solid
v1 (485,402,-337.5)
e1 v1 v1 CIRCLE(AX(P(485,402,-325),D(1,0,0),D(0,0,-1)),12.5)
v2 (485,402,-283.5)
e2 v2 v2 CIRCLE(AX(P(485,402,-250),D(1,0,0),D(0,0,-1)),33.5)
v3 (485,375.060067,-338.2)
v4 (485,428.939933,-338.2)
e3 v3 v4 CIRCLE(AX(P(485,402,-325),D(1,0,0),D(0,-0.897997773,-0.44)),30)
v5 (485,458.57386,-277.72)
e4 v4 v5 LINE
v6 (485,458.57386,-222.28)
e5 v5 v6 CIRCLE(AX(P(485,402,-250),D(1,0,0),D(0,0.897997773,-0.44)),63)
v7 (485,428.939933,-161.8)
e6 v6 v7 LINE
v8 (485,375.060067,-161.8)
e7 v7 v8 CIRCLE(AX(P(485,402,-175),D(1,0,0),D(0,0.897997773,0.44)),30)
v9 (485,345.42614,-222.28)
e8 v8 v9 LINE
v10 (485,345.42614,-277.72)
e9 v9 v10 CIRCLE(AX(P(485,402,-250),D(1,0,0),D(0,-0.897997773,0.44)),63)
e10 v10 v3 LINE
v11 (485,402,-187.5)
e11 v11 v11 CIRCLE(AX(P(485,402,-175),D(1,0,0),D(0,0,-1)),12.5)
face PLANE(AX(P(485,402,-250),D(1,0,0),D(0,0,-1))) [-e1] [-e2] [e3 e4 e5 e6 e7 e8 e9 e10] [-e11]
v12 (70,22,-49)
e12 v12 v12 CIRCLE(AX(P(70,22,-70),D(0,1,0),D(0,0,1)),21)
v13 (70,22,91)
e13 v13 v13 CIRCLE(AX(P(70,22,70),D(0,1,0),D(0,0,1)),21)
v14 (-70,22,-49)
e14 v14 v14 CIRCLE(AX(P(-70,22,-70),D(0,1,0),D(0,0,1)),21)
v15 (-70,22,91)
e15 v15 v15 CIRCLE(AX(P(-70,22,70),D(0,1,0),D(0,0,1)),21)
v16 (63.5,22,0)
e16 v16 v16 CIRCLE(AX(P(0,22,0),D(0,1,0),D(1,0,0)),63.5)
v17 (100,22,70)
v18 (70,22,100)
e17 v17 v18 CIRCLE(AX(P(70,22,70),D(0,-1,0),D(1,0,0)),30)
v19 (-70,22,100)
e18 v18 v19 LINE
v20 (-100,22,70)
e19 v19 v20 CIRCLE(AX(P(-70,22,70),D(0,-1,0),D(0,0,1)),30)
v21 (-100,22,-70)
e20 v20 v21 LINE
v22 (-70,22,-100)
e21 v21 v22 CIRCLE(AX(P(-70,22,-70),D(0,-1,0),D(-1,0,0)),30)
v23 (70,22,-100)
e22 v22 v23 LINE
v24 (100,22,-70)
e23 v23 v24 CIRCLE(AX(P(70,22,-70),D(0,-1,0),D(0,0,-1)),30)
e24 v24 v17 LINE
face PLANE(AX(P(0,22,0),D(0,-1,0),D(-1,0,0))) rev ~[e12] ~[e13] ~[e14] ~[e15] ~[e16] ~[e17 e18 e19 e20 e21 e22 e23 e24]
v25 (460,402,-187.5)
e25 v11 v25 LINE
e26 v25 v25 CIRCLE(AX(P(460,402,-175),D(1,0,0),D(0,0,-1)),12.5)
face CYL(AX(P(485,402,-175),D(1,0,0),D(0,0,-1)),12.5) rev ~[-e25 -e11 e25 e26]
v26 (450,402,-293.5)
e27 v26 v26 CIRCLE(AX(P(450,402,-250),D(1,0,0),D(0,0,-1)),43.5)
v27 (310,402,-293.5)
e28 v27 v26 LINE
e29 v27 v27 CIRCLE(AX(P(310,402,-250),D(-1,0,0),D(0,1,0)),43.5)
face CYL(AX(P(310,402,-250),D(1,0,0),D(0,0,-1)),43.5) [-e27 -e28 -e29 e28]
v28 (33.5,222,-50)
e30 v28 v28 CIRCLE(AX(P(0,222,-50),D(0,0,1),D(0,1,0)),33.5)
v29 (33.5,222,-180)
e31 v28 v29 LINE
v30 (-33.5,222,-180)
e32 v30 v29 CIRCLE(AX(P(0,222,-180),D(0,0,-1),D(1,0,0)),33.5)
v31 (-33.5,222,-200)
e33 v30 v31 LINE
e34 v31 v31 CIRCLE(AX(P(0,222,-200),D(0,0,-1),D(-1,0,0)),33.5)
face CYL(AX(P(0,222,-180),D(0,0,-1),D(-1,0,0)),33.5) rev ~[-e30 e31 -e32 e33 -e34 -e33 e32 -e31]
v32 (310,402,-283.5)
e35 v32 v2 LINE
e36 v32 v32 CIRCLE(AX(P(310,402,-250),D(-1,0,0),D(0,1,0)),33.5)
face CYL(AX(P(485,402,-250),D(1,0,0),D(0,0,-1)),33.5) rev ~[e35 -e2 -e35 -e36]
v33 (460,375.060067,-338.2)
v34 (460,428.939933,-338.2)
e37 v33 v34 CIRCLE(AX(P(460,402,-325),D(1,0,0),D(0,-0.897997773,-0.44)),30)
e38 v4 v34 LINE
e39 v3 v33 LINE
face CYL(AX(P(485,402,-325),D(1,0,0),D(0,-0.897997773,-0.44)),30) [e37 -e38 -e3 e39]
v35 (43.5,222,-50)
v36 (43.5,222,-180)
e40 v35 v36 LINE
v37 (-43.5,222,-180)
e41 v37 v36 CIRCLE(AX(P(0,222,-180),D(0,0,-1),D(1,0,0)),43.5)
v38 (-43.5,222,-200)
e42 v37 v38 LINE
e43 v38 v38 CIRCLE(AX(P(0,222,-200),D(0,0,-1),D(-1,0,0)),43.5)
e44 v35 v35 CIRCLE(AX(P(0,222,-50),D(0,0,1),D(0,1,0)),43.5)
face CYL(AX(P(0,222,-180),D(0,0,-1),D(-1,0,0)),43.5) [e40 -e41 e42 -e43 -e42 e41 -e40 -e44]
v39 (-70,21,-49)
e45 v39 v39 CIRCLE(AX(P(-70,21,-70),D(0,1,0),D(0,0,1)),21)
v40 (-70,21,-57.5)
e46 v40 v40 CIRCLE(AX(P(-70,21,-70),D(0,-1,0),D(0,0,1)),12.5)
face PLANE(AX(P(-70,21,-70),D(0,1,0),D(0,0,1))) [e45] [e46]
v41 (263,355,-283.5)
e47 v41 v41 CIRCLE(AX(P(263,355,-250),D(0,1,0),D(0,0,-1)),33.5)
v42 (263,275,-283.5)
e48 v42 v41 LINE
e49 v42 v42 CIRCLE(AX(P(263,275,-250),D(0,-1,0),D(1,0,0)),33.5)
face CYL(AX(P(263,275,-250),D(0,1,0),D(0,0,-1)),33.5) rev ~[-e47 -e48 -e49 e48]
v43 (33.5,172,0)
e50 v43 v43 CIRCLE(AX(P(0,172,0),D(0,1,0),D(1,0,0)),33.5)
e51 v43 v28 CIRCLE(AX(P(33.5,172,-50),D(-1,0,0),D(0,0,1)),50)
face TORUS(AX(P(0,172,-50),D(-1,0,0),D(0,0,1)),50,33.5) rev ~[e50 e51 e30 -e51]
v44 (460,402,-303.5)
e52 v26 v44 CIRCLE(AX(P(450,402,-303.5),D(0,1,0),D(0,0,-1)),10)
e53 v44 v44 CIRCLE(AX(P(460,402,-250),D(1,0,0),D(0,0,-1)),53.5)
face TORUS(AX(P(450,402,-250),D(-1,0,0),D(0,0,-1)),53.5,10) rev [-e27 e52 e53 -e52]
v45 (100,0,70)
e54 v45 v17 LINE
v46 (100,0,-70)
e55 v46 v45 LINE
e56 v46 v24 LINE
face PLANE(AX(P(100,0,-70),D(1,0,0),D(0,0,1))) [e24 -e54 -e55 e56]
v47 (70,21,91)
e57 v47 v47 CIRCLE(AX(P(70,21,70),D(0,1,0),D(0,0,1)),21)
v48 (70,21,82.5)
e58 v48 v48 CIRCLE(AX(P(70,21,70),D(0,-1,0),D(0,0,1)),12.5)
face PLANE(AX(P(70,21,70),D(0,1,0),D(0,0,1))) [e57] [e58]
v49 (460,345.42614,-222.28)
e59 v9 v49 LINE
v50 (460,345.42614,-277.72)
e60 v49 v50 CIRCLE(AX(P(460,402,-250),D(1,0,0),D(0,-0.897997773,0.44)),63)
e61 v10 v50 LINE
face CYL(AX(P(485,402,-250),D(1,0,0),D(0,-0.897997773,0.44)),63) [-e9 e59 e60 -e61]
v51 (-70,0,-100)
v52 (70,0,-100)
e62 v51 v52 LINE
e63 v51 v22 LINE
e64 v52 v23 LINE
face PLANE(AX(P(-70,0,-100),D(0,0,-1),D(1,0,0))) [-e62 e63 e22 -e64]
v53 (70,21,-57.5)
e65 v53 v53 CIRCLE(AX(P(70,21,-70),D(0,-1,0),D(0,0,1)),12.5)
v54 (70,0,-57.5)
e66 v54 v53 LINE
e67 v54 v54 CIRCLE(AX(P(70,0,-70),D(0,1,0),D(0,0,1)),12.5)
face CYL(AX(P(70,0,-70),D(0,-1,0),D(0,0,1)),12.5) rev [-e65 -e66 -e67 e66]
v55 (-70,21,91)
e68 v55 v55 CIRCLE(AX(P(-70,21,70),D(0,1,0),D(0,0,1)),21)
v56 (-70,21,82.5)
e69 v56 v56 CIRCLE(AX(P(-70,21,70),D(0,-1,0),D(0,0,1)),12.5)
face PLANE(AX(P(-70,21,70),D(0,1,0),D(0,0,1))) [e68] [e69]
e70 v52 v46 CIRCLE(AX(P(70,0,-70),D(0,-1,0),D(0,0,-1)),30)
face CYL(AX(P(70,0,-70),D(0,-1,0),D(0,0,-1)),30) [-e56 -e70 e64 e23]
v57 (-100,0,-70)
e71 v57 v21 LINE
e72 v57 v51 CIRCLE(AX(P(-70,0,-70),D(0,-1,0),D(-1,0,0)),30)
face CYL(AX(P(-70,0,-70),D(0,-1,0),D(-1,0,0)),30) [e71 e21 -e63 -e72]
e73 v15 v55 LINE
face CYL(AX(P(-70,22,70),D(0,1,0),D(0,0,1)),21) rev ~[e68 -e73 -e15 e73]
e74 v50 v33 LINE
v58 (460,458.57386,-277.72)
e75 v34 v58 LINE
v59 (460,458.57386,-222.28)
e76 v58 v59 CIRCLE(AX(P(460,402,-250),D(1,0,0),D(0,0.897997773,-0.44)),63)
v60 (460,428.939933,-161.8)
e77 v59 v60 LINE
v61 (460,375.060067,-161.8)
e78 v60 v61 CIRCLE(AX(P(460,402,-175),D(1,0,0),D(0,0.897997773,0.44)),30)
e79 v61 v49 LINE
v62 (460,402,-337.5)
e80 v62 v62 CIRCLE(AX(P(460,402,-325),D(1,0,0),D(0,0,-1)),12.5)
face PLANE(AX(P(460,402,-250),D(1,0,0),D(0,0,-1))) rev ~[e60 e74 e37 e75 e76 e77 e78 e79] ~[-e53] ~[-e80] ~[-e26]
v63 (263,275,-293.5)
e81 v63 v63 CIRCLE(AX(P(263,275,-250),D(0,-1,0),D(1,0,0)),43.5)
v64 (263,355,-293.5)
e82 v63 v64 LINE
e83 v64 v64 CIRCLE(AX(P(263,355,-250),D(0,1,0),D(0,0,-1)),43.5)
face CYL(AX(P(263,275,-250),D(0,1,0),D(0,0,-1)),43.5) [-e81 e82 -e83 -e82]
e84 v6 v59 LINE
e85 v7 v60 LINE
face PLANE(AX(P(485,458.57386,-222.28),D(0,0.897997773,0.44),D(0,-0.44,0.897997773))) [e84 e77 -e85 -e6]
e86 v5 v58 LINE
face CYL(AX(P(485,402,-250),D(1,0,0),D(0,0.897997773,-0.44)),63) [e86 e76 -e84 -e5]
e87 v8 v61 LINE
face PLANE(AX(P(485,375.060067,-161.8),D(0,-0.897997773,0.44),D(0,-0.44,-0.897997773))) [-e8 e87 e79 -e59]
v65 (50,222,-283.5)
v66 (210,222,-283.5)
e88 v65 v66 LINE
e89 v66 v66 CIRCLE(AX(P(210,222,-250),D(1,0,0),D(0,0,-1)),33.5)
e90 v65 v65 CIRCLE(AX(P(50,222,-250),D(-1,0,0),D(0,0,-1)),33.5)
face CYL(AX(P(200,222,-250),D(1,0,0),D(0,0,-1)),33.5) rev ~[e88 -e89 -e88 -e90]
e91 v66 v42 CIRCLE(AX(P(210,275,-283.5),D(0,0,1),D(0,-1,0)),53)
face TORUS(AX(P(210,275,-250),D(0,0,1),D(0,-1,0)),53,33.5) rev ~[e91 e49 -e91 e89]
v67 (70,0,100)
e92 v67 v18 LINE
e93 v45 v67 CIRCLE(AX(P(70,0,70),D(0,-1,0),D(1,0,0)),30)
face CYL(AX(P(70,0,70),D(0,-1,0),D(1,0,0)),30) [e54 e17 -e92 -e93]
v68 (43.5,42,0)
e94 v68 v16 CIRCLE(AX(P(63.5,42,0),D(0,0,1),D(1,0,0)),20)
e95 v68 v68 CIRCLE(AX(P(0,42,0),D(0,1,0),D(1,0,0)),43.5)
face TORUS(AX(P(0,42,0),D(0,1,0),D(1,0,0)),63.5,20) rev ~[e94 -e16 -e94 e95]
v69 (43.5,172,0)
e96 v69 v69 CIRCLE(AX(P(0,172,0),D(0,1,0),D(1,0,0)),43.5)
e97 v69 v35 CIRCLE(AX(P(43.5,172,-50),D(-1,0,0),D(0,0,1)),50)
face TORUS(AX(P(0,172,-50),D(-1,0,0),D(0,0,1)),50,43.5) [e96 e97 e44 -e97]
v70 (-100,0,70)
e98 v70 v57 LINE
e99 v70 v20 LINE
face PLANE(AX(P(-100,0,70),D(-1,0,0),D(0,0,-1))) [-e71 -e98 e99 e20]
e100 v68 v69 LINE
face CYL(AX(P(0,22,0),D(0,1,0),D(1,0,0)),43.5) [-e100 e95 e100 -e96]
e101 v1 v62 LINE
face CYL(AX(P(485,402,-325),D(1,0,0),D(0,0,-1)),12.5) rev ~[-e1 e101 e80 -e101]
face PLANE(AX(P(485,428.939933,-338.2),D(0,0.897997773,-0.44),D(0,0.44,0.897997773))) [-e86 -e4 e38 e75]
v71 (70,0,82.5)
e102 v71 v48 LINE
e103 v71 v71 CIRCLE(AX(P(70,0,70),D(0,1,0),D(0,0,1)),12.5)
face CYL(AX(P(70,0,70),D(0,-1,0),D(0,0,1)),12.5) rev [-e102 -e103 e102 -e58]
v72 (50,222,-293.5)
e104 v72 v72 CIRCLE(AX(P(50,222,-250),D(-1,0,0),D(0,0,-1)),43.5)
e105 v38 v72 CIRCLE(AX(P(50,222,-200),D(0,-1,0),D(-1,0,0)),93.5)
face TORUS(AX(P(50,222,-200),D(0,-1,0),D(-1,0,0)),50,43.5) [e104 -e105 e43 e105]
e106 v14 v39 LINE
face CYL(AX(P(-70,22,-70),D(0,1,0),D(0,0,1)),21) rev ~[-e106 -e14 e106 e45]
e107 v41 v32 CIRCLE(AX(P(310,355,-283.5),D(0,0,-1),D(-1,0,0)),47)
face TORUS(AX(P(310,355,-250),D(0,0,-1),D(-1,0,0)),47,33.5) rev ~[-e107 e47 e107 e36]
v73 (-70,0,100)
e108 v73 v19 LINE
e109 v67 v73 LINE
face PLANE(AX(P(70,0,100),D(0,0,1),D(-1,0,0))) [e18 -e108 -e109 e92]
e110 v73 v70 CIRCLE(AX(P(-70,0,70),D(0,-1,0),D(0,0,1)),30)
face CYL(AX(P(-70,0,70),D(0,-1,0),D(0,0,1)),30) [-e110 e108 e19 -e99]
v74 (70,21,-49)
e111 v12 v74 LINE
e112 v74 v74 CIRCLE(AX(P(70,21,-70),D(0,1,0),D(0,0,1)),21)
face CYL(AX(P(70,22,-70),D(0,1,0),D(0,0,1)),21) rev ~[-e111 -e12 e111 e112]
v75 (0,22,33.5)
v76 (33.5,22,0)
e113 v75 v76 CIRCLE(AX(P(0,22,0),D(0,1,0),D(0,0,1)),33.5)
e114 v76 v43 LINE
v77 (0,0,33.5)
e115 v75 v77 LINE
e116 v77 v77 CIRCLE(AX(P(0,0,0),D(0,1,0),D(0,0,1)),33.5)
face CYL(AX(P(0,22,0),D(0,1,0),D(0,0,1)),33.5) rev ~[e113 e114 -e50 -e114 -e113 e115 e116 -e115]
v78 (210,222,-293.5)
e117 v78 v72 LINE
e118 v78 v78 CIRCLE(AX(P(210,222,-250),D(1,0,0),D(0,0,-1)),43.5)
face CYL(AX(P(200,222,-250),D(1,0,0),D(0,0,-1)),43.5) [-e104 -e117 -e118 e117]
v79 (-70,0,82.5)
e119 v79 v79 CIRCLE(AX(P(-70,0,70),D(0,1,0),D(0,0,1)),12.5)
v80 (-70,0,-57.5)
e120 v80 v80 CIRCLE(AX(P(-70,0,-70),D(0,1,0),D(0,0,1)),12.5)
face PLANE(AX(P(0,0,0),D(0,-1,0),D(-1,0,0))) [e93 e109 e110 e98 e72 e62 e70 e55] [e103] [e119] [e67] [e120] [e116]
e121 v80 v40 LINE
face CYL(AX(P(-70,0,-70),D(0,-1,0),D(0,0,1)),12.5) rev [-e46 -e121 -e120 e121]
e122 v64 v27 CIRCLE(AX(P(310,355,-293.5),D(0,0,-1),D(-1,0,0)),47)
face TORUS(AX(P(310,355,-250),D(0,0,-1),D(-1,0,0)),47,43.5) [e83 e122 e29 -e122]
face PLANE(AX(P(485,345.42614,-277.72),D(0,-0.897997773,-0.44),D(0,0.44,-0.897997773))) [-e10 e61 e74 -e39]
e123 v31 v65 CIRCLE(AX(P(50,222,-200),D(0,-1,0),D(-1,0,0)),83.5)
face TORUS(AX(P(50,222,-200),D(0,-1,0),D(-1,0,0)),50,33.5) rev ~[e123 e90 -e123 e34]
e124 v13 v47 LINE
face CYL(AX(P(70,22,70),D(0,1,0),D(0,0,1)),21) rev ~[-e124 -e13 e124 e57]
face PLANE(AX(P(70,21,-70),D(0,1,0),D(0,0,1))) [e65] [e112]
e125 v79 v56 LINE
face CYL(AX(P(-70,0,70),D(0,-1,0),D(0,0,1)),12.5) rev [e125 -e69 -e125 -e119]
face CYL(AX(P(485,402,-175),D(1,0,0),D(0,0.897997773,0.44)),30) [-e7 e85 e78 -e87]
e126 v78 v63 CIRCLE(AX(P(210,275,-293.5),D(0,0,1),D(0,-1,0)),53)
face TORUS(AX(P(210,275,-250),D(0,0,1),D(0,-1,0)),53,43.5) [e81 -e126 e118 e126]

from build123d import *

# Parameters (mm, degrees)
INLET_FLANGE_SKETCH_R         = 12.5
INLET_FLANGE_200X200X22_DEPTH = 22
BOLT_SPOTFACE_SKETCH_R        = 21
BOLT_SPOTFACES_4X_42_DEPTH    = 1
INLET_BORE_SKETCH_R           = 33.5
INLET_BORE_67_DEPTH           = 25
PIPE_SECTION_1_PROFILE_R      = 43.5
PIPE_SECTION_1_PROFILE_R_2    = 33.5
PIPE_SECTION_2_PROFILE_R      = 43.5
PIPE_SECTION_2_PROFILE_R_2    = 33.5
S_BEND_PROFILE_R              = 43.5
S_BEND_PROFILE_R_2            = 33.5
OUTLET_START                  = 25
OUTLET_FLANGE_SKETCH_R        = 33.5
OUTLET_FLANGE_SKETCH_R_2      = 12.5
OUTLET_FLANGE_DEPTH           = 25
INLET_FLANGE_FILLET_R20_R     = 20
OUTLET_FILLET_R10_R           = 10


with BuildPart() as part:
    # Inlet Flange Sketch → Inlet Flange 200x200x22 (new body)
    with BuildSketch(Plane(origin=(0, 0, 0), x_dir=(1, 0, 0), z_dir=(0, 1, 0))):
        with BuildLine():
            Line((-70, 100), (70, 100))
            ThreePointArc((70, 100), (91.213203436, 91.213203436), (100, 70))
            Line((100, 70), (100, -70))
            ThreePointArc((100, -70), (91.213203436, -91.213203436), (70, -100))
            Line((70, -100), (-70, -100))
            ThreePointArc((-70, -100), (-91.213203436, -91.213203436), (-100, -70))
            Line((-100, -70), (-100, 70))
            ThreePointArc((-100, 70), (-91.213203436, 91.213203436), (-70, 100))
        make_face()
        with Locations(Location((-70, 70, 0), (0, 0, 270))):
            Circle(INLET_FLANGE_SKETCH_R, mode=Mode.SUBTRACT)
        with Locations(Location((70, 70, 0), (0, 0, 270))):
            Circle(INLET_FLANGE_SKETCH_R, mode=Mode.SUBTRACT)
        with Locations(Location((70, -70, 0), (0, 0, 270))):
            Circle(INLET_FLANGE_SKETCH_R, mode=Mode.SUBTRACT)
        with Locations(Location((-70, -70, 0), (0, 0, 270))):
            Circle(INLET_FLANGE_SKETCH_R, mode=Mode.SUBTRACT)
    extrude(amount=INLET_FLANGE_200X200X22_DEPTH)

    # Bolt Spotface Sketch → Bolt Spotfaces 4xØ42 (cut)
    with BuildSketch(Plane(origin=(0, 22, 0), x_dir=(1, 0, 0), z_dir=(0, 1, 0))):
        with Locations(Location((-70, 70, 0), (0, 0, 270))):
            Circle(BOLT_SPOTFACE_SKETCH_R)
        with Locations(Location((70, 70, 0), (0, 0, 270))):
            Circle(BOLT_SPOTFACE_SKETCH_R)
        with Locations(Location((70, -70, 0), (0, 0, 270))):
            Circle(BOLT_SPOTFACE_SKETCH_R)
        with Locations(Location((-70, -70, 0), (0, 0, 270))):
            Circle(BOLT_SPOTFACE_SKETCH_R)
    extrude(amount=-BOLT_SPOTFACES_4X_42_DEPTH, mode=Mode.SUBTRACT)

    # Inlet Bore Sketch → Inlet Bore Ø67 (cut)
    with BuildSketch(Plane(origin=(0, 22, 0), x_dir=(1, 0, 0), z_dir=(0, 1, 0))):
        with Locations(Location((0, 0, 0), (0, 0, 270))):
            Circle(INLET_BORE_SKETCH_R)
    extrude(amount=-INLET_BORE_67_DEPTH, mode=Mode.SUBTRACT)

    # Pipe Section 1: sweep along a path in Pipe Section 1 Path
    with BuildLine(Plane(origin=(0, 0, 0), x_dir=(0, 0, -1), z_dir=(1, 0, 0))) as pipe_section_1_path:
        Line((0, 22), (0, 172))
        ThreePointArc((0, 172), (14.644660941, 207.355339059), (50, 222))
        Line((50, 222), (180, 222))
    # Pipe Section 1 Profile → Pipe Section 1 (sweep)
    with BuildSketch(Plane(origin=(0, 22, 0), x_dir=(1, 0, 0), z_dir=(0, 1, 0))):
        Circle(PIPE_SECTION_1_PROFILE_R)
        Circle(PIPE_SECTION_1_PROFILE_R_2, mode=Mode.SUBTRACT)
    sweep(path=pipe_section_1_path.line)

    # Pipe Section 2: sweep along a path in Pipe Section 2 Path
    with BuildLine(Plane(origin=(0, 225, 0), x_dir=(1, 0, 0), z_dir=(0, 1, 0))) as pipe_section_2_path:
        Line((0, 180), (0, 200))
        ThreePointArc((0, 200), (14.644660941, 235.355339059), (50, 250))
        Line((50, 250), (200, 250))
    # Pipe Section 2 Profile → Pipe Section 2 (sweep)
    with BuildSketch(Plane(origin=(0, 0, -180), x_dir=(-1, 0, 0), z_dir=(0, 0, -1))):
        with Locations((0, 222)):
            Circle(PIPE_SECTION_2_PROFILE_R)
        with Locations((0, 222)):
            Circle(PIPE_SECTION_2_PROFILE_R_2, mode=Mode.SUBTRACT)
    sweep(path=pipe_section_2_path.line)

    # S-Bend Pipe Section: sweep along a path in S-Bend Path
    with BuildLine(Plane.XY.offset(-250)) as s_bend_pipe_section_path:
        Line((200, 225), (210, 225))
        ThreePointArc((210, 225), (245.355339059, 239.644660941), (260, 275))
        Line((260, 275), (260, 355))
        ThreePointArc((260, 355), (274.644660941, 390.355339059), (310, 405))
        Line((310, 405), (460, 405))
    # S-Bend Profile → S-Bend Pipe Section (sweep)
    with BuildSketch(Plane(origin=(200, 0, 0), x_dir=(0, 0, -1), z_dir=(1, 0, 0))):
        with Locations((250, 222)):
            Circle(S_BEND_PROFILE_R)
        with Locations((250, 222)):
            Circle(S_BEND_PROFILE_R_2, mode=Mode.SUBTRACT)
    sweep(path=s_bend_pipe_section_path.line)

    # Outlet Flange Sketch → Outlet Flange (add)
    with BuildSketch(Plane(origin=(460, 0, 0), x_dir=(0, 0, -1), z_dir=(1, 0, 0)).offset(OUTLET_START)):
        with BuildLine():
            Line((222.28, 458.573859688), (161.8, 428.939933185))
            ThreePointArc((161.8, 428.939933185), (145, 402), (161.8, 375.060066815))
            Line((161.8, 375.060066815), (222.28, 345.426140312))
            ThreePointArc((222.28, 345.426140312), (250, 339), (277.72, 345.426140312))
            Line((277.72, 345.426140312), (338.2, 375.060066815))
            ThreePointArc((338.2, 375.060066815), (355, 402), (338.2, 428.939933185))
            Line((338.2, 428.939933185), (277.72, 458.573859688))
            ThreePointArc((277.72, 458.573859688), (250, 465), (222.28, 458.573859688))
        make_face()
        with Locations((250, 402)):
            Circle(OUTLET_FLANGE_SKETCH_R, mode=Mode.SUBTRACT)
        with Locations((325, 402)):
            Circle(OUTLET_FLANGE_SKETCH_R_2, mode=Mode.SUBTRACT)
        with Locations((175, 402)):
            Circle(OUTLET_FLANGE_SKETCH_R_2, mode=Mode.SUBTRACT)
    extrude(amount=-OUTLET_FLANGE_DEPTH)

    # Inlet Flange Fillet R20
    inlet_flange_fillet_r20_edges = [part.edges().sort_by_distance(p)[0] for p in [
        (-43.5, 22, 0),
    ]]
    fillet(inlet_flange_fillet_r20_edges, radius=INLET_FLANGE_FILLET_R20_R)

    # Outlet Fillet R10
    outlet_fillet_r10_edges = [part.edges().sort_by_distance(p)[0] for p in [
        (460, 402, -206.5),
    ]]
    fillet(outlet_fillet_r10_edges, radius=OUTLET_FILLET_R10_R)


solid = part.part
